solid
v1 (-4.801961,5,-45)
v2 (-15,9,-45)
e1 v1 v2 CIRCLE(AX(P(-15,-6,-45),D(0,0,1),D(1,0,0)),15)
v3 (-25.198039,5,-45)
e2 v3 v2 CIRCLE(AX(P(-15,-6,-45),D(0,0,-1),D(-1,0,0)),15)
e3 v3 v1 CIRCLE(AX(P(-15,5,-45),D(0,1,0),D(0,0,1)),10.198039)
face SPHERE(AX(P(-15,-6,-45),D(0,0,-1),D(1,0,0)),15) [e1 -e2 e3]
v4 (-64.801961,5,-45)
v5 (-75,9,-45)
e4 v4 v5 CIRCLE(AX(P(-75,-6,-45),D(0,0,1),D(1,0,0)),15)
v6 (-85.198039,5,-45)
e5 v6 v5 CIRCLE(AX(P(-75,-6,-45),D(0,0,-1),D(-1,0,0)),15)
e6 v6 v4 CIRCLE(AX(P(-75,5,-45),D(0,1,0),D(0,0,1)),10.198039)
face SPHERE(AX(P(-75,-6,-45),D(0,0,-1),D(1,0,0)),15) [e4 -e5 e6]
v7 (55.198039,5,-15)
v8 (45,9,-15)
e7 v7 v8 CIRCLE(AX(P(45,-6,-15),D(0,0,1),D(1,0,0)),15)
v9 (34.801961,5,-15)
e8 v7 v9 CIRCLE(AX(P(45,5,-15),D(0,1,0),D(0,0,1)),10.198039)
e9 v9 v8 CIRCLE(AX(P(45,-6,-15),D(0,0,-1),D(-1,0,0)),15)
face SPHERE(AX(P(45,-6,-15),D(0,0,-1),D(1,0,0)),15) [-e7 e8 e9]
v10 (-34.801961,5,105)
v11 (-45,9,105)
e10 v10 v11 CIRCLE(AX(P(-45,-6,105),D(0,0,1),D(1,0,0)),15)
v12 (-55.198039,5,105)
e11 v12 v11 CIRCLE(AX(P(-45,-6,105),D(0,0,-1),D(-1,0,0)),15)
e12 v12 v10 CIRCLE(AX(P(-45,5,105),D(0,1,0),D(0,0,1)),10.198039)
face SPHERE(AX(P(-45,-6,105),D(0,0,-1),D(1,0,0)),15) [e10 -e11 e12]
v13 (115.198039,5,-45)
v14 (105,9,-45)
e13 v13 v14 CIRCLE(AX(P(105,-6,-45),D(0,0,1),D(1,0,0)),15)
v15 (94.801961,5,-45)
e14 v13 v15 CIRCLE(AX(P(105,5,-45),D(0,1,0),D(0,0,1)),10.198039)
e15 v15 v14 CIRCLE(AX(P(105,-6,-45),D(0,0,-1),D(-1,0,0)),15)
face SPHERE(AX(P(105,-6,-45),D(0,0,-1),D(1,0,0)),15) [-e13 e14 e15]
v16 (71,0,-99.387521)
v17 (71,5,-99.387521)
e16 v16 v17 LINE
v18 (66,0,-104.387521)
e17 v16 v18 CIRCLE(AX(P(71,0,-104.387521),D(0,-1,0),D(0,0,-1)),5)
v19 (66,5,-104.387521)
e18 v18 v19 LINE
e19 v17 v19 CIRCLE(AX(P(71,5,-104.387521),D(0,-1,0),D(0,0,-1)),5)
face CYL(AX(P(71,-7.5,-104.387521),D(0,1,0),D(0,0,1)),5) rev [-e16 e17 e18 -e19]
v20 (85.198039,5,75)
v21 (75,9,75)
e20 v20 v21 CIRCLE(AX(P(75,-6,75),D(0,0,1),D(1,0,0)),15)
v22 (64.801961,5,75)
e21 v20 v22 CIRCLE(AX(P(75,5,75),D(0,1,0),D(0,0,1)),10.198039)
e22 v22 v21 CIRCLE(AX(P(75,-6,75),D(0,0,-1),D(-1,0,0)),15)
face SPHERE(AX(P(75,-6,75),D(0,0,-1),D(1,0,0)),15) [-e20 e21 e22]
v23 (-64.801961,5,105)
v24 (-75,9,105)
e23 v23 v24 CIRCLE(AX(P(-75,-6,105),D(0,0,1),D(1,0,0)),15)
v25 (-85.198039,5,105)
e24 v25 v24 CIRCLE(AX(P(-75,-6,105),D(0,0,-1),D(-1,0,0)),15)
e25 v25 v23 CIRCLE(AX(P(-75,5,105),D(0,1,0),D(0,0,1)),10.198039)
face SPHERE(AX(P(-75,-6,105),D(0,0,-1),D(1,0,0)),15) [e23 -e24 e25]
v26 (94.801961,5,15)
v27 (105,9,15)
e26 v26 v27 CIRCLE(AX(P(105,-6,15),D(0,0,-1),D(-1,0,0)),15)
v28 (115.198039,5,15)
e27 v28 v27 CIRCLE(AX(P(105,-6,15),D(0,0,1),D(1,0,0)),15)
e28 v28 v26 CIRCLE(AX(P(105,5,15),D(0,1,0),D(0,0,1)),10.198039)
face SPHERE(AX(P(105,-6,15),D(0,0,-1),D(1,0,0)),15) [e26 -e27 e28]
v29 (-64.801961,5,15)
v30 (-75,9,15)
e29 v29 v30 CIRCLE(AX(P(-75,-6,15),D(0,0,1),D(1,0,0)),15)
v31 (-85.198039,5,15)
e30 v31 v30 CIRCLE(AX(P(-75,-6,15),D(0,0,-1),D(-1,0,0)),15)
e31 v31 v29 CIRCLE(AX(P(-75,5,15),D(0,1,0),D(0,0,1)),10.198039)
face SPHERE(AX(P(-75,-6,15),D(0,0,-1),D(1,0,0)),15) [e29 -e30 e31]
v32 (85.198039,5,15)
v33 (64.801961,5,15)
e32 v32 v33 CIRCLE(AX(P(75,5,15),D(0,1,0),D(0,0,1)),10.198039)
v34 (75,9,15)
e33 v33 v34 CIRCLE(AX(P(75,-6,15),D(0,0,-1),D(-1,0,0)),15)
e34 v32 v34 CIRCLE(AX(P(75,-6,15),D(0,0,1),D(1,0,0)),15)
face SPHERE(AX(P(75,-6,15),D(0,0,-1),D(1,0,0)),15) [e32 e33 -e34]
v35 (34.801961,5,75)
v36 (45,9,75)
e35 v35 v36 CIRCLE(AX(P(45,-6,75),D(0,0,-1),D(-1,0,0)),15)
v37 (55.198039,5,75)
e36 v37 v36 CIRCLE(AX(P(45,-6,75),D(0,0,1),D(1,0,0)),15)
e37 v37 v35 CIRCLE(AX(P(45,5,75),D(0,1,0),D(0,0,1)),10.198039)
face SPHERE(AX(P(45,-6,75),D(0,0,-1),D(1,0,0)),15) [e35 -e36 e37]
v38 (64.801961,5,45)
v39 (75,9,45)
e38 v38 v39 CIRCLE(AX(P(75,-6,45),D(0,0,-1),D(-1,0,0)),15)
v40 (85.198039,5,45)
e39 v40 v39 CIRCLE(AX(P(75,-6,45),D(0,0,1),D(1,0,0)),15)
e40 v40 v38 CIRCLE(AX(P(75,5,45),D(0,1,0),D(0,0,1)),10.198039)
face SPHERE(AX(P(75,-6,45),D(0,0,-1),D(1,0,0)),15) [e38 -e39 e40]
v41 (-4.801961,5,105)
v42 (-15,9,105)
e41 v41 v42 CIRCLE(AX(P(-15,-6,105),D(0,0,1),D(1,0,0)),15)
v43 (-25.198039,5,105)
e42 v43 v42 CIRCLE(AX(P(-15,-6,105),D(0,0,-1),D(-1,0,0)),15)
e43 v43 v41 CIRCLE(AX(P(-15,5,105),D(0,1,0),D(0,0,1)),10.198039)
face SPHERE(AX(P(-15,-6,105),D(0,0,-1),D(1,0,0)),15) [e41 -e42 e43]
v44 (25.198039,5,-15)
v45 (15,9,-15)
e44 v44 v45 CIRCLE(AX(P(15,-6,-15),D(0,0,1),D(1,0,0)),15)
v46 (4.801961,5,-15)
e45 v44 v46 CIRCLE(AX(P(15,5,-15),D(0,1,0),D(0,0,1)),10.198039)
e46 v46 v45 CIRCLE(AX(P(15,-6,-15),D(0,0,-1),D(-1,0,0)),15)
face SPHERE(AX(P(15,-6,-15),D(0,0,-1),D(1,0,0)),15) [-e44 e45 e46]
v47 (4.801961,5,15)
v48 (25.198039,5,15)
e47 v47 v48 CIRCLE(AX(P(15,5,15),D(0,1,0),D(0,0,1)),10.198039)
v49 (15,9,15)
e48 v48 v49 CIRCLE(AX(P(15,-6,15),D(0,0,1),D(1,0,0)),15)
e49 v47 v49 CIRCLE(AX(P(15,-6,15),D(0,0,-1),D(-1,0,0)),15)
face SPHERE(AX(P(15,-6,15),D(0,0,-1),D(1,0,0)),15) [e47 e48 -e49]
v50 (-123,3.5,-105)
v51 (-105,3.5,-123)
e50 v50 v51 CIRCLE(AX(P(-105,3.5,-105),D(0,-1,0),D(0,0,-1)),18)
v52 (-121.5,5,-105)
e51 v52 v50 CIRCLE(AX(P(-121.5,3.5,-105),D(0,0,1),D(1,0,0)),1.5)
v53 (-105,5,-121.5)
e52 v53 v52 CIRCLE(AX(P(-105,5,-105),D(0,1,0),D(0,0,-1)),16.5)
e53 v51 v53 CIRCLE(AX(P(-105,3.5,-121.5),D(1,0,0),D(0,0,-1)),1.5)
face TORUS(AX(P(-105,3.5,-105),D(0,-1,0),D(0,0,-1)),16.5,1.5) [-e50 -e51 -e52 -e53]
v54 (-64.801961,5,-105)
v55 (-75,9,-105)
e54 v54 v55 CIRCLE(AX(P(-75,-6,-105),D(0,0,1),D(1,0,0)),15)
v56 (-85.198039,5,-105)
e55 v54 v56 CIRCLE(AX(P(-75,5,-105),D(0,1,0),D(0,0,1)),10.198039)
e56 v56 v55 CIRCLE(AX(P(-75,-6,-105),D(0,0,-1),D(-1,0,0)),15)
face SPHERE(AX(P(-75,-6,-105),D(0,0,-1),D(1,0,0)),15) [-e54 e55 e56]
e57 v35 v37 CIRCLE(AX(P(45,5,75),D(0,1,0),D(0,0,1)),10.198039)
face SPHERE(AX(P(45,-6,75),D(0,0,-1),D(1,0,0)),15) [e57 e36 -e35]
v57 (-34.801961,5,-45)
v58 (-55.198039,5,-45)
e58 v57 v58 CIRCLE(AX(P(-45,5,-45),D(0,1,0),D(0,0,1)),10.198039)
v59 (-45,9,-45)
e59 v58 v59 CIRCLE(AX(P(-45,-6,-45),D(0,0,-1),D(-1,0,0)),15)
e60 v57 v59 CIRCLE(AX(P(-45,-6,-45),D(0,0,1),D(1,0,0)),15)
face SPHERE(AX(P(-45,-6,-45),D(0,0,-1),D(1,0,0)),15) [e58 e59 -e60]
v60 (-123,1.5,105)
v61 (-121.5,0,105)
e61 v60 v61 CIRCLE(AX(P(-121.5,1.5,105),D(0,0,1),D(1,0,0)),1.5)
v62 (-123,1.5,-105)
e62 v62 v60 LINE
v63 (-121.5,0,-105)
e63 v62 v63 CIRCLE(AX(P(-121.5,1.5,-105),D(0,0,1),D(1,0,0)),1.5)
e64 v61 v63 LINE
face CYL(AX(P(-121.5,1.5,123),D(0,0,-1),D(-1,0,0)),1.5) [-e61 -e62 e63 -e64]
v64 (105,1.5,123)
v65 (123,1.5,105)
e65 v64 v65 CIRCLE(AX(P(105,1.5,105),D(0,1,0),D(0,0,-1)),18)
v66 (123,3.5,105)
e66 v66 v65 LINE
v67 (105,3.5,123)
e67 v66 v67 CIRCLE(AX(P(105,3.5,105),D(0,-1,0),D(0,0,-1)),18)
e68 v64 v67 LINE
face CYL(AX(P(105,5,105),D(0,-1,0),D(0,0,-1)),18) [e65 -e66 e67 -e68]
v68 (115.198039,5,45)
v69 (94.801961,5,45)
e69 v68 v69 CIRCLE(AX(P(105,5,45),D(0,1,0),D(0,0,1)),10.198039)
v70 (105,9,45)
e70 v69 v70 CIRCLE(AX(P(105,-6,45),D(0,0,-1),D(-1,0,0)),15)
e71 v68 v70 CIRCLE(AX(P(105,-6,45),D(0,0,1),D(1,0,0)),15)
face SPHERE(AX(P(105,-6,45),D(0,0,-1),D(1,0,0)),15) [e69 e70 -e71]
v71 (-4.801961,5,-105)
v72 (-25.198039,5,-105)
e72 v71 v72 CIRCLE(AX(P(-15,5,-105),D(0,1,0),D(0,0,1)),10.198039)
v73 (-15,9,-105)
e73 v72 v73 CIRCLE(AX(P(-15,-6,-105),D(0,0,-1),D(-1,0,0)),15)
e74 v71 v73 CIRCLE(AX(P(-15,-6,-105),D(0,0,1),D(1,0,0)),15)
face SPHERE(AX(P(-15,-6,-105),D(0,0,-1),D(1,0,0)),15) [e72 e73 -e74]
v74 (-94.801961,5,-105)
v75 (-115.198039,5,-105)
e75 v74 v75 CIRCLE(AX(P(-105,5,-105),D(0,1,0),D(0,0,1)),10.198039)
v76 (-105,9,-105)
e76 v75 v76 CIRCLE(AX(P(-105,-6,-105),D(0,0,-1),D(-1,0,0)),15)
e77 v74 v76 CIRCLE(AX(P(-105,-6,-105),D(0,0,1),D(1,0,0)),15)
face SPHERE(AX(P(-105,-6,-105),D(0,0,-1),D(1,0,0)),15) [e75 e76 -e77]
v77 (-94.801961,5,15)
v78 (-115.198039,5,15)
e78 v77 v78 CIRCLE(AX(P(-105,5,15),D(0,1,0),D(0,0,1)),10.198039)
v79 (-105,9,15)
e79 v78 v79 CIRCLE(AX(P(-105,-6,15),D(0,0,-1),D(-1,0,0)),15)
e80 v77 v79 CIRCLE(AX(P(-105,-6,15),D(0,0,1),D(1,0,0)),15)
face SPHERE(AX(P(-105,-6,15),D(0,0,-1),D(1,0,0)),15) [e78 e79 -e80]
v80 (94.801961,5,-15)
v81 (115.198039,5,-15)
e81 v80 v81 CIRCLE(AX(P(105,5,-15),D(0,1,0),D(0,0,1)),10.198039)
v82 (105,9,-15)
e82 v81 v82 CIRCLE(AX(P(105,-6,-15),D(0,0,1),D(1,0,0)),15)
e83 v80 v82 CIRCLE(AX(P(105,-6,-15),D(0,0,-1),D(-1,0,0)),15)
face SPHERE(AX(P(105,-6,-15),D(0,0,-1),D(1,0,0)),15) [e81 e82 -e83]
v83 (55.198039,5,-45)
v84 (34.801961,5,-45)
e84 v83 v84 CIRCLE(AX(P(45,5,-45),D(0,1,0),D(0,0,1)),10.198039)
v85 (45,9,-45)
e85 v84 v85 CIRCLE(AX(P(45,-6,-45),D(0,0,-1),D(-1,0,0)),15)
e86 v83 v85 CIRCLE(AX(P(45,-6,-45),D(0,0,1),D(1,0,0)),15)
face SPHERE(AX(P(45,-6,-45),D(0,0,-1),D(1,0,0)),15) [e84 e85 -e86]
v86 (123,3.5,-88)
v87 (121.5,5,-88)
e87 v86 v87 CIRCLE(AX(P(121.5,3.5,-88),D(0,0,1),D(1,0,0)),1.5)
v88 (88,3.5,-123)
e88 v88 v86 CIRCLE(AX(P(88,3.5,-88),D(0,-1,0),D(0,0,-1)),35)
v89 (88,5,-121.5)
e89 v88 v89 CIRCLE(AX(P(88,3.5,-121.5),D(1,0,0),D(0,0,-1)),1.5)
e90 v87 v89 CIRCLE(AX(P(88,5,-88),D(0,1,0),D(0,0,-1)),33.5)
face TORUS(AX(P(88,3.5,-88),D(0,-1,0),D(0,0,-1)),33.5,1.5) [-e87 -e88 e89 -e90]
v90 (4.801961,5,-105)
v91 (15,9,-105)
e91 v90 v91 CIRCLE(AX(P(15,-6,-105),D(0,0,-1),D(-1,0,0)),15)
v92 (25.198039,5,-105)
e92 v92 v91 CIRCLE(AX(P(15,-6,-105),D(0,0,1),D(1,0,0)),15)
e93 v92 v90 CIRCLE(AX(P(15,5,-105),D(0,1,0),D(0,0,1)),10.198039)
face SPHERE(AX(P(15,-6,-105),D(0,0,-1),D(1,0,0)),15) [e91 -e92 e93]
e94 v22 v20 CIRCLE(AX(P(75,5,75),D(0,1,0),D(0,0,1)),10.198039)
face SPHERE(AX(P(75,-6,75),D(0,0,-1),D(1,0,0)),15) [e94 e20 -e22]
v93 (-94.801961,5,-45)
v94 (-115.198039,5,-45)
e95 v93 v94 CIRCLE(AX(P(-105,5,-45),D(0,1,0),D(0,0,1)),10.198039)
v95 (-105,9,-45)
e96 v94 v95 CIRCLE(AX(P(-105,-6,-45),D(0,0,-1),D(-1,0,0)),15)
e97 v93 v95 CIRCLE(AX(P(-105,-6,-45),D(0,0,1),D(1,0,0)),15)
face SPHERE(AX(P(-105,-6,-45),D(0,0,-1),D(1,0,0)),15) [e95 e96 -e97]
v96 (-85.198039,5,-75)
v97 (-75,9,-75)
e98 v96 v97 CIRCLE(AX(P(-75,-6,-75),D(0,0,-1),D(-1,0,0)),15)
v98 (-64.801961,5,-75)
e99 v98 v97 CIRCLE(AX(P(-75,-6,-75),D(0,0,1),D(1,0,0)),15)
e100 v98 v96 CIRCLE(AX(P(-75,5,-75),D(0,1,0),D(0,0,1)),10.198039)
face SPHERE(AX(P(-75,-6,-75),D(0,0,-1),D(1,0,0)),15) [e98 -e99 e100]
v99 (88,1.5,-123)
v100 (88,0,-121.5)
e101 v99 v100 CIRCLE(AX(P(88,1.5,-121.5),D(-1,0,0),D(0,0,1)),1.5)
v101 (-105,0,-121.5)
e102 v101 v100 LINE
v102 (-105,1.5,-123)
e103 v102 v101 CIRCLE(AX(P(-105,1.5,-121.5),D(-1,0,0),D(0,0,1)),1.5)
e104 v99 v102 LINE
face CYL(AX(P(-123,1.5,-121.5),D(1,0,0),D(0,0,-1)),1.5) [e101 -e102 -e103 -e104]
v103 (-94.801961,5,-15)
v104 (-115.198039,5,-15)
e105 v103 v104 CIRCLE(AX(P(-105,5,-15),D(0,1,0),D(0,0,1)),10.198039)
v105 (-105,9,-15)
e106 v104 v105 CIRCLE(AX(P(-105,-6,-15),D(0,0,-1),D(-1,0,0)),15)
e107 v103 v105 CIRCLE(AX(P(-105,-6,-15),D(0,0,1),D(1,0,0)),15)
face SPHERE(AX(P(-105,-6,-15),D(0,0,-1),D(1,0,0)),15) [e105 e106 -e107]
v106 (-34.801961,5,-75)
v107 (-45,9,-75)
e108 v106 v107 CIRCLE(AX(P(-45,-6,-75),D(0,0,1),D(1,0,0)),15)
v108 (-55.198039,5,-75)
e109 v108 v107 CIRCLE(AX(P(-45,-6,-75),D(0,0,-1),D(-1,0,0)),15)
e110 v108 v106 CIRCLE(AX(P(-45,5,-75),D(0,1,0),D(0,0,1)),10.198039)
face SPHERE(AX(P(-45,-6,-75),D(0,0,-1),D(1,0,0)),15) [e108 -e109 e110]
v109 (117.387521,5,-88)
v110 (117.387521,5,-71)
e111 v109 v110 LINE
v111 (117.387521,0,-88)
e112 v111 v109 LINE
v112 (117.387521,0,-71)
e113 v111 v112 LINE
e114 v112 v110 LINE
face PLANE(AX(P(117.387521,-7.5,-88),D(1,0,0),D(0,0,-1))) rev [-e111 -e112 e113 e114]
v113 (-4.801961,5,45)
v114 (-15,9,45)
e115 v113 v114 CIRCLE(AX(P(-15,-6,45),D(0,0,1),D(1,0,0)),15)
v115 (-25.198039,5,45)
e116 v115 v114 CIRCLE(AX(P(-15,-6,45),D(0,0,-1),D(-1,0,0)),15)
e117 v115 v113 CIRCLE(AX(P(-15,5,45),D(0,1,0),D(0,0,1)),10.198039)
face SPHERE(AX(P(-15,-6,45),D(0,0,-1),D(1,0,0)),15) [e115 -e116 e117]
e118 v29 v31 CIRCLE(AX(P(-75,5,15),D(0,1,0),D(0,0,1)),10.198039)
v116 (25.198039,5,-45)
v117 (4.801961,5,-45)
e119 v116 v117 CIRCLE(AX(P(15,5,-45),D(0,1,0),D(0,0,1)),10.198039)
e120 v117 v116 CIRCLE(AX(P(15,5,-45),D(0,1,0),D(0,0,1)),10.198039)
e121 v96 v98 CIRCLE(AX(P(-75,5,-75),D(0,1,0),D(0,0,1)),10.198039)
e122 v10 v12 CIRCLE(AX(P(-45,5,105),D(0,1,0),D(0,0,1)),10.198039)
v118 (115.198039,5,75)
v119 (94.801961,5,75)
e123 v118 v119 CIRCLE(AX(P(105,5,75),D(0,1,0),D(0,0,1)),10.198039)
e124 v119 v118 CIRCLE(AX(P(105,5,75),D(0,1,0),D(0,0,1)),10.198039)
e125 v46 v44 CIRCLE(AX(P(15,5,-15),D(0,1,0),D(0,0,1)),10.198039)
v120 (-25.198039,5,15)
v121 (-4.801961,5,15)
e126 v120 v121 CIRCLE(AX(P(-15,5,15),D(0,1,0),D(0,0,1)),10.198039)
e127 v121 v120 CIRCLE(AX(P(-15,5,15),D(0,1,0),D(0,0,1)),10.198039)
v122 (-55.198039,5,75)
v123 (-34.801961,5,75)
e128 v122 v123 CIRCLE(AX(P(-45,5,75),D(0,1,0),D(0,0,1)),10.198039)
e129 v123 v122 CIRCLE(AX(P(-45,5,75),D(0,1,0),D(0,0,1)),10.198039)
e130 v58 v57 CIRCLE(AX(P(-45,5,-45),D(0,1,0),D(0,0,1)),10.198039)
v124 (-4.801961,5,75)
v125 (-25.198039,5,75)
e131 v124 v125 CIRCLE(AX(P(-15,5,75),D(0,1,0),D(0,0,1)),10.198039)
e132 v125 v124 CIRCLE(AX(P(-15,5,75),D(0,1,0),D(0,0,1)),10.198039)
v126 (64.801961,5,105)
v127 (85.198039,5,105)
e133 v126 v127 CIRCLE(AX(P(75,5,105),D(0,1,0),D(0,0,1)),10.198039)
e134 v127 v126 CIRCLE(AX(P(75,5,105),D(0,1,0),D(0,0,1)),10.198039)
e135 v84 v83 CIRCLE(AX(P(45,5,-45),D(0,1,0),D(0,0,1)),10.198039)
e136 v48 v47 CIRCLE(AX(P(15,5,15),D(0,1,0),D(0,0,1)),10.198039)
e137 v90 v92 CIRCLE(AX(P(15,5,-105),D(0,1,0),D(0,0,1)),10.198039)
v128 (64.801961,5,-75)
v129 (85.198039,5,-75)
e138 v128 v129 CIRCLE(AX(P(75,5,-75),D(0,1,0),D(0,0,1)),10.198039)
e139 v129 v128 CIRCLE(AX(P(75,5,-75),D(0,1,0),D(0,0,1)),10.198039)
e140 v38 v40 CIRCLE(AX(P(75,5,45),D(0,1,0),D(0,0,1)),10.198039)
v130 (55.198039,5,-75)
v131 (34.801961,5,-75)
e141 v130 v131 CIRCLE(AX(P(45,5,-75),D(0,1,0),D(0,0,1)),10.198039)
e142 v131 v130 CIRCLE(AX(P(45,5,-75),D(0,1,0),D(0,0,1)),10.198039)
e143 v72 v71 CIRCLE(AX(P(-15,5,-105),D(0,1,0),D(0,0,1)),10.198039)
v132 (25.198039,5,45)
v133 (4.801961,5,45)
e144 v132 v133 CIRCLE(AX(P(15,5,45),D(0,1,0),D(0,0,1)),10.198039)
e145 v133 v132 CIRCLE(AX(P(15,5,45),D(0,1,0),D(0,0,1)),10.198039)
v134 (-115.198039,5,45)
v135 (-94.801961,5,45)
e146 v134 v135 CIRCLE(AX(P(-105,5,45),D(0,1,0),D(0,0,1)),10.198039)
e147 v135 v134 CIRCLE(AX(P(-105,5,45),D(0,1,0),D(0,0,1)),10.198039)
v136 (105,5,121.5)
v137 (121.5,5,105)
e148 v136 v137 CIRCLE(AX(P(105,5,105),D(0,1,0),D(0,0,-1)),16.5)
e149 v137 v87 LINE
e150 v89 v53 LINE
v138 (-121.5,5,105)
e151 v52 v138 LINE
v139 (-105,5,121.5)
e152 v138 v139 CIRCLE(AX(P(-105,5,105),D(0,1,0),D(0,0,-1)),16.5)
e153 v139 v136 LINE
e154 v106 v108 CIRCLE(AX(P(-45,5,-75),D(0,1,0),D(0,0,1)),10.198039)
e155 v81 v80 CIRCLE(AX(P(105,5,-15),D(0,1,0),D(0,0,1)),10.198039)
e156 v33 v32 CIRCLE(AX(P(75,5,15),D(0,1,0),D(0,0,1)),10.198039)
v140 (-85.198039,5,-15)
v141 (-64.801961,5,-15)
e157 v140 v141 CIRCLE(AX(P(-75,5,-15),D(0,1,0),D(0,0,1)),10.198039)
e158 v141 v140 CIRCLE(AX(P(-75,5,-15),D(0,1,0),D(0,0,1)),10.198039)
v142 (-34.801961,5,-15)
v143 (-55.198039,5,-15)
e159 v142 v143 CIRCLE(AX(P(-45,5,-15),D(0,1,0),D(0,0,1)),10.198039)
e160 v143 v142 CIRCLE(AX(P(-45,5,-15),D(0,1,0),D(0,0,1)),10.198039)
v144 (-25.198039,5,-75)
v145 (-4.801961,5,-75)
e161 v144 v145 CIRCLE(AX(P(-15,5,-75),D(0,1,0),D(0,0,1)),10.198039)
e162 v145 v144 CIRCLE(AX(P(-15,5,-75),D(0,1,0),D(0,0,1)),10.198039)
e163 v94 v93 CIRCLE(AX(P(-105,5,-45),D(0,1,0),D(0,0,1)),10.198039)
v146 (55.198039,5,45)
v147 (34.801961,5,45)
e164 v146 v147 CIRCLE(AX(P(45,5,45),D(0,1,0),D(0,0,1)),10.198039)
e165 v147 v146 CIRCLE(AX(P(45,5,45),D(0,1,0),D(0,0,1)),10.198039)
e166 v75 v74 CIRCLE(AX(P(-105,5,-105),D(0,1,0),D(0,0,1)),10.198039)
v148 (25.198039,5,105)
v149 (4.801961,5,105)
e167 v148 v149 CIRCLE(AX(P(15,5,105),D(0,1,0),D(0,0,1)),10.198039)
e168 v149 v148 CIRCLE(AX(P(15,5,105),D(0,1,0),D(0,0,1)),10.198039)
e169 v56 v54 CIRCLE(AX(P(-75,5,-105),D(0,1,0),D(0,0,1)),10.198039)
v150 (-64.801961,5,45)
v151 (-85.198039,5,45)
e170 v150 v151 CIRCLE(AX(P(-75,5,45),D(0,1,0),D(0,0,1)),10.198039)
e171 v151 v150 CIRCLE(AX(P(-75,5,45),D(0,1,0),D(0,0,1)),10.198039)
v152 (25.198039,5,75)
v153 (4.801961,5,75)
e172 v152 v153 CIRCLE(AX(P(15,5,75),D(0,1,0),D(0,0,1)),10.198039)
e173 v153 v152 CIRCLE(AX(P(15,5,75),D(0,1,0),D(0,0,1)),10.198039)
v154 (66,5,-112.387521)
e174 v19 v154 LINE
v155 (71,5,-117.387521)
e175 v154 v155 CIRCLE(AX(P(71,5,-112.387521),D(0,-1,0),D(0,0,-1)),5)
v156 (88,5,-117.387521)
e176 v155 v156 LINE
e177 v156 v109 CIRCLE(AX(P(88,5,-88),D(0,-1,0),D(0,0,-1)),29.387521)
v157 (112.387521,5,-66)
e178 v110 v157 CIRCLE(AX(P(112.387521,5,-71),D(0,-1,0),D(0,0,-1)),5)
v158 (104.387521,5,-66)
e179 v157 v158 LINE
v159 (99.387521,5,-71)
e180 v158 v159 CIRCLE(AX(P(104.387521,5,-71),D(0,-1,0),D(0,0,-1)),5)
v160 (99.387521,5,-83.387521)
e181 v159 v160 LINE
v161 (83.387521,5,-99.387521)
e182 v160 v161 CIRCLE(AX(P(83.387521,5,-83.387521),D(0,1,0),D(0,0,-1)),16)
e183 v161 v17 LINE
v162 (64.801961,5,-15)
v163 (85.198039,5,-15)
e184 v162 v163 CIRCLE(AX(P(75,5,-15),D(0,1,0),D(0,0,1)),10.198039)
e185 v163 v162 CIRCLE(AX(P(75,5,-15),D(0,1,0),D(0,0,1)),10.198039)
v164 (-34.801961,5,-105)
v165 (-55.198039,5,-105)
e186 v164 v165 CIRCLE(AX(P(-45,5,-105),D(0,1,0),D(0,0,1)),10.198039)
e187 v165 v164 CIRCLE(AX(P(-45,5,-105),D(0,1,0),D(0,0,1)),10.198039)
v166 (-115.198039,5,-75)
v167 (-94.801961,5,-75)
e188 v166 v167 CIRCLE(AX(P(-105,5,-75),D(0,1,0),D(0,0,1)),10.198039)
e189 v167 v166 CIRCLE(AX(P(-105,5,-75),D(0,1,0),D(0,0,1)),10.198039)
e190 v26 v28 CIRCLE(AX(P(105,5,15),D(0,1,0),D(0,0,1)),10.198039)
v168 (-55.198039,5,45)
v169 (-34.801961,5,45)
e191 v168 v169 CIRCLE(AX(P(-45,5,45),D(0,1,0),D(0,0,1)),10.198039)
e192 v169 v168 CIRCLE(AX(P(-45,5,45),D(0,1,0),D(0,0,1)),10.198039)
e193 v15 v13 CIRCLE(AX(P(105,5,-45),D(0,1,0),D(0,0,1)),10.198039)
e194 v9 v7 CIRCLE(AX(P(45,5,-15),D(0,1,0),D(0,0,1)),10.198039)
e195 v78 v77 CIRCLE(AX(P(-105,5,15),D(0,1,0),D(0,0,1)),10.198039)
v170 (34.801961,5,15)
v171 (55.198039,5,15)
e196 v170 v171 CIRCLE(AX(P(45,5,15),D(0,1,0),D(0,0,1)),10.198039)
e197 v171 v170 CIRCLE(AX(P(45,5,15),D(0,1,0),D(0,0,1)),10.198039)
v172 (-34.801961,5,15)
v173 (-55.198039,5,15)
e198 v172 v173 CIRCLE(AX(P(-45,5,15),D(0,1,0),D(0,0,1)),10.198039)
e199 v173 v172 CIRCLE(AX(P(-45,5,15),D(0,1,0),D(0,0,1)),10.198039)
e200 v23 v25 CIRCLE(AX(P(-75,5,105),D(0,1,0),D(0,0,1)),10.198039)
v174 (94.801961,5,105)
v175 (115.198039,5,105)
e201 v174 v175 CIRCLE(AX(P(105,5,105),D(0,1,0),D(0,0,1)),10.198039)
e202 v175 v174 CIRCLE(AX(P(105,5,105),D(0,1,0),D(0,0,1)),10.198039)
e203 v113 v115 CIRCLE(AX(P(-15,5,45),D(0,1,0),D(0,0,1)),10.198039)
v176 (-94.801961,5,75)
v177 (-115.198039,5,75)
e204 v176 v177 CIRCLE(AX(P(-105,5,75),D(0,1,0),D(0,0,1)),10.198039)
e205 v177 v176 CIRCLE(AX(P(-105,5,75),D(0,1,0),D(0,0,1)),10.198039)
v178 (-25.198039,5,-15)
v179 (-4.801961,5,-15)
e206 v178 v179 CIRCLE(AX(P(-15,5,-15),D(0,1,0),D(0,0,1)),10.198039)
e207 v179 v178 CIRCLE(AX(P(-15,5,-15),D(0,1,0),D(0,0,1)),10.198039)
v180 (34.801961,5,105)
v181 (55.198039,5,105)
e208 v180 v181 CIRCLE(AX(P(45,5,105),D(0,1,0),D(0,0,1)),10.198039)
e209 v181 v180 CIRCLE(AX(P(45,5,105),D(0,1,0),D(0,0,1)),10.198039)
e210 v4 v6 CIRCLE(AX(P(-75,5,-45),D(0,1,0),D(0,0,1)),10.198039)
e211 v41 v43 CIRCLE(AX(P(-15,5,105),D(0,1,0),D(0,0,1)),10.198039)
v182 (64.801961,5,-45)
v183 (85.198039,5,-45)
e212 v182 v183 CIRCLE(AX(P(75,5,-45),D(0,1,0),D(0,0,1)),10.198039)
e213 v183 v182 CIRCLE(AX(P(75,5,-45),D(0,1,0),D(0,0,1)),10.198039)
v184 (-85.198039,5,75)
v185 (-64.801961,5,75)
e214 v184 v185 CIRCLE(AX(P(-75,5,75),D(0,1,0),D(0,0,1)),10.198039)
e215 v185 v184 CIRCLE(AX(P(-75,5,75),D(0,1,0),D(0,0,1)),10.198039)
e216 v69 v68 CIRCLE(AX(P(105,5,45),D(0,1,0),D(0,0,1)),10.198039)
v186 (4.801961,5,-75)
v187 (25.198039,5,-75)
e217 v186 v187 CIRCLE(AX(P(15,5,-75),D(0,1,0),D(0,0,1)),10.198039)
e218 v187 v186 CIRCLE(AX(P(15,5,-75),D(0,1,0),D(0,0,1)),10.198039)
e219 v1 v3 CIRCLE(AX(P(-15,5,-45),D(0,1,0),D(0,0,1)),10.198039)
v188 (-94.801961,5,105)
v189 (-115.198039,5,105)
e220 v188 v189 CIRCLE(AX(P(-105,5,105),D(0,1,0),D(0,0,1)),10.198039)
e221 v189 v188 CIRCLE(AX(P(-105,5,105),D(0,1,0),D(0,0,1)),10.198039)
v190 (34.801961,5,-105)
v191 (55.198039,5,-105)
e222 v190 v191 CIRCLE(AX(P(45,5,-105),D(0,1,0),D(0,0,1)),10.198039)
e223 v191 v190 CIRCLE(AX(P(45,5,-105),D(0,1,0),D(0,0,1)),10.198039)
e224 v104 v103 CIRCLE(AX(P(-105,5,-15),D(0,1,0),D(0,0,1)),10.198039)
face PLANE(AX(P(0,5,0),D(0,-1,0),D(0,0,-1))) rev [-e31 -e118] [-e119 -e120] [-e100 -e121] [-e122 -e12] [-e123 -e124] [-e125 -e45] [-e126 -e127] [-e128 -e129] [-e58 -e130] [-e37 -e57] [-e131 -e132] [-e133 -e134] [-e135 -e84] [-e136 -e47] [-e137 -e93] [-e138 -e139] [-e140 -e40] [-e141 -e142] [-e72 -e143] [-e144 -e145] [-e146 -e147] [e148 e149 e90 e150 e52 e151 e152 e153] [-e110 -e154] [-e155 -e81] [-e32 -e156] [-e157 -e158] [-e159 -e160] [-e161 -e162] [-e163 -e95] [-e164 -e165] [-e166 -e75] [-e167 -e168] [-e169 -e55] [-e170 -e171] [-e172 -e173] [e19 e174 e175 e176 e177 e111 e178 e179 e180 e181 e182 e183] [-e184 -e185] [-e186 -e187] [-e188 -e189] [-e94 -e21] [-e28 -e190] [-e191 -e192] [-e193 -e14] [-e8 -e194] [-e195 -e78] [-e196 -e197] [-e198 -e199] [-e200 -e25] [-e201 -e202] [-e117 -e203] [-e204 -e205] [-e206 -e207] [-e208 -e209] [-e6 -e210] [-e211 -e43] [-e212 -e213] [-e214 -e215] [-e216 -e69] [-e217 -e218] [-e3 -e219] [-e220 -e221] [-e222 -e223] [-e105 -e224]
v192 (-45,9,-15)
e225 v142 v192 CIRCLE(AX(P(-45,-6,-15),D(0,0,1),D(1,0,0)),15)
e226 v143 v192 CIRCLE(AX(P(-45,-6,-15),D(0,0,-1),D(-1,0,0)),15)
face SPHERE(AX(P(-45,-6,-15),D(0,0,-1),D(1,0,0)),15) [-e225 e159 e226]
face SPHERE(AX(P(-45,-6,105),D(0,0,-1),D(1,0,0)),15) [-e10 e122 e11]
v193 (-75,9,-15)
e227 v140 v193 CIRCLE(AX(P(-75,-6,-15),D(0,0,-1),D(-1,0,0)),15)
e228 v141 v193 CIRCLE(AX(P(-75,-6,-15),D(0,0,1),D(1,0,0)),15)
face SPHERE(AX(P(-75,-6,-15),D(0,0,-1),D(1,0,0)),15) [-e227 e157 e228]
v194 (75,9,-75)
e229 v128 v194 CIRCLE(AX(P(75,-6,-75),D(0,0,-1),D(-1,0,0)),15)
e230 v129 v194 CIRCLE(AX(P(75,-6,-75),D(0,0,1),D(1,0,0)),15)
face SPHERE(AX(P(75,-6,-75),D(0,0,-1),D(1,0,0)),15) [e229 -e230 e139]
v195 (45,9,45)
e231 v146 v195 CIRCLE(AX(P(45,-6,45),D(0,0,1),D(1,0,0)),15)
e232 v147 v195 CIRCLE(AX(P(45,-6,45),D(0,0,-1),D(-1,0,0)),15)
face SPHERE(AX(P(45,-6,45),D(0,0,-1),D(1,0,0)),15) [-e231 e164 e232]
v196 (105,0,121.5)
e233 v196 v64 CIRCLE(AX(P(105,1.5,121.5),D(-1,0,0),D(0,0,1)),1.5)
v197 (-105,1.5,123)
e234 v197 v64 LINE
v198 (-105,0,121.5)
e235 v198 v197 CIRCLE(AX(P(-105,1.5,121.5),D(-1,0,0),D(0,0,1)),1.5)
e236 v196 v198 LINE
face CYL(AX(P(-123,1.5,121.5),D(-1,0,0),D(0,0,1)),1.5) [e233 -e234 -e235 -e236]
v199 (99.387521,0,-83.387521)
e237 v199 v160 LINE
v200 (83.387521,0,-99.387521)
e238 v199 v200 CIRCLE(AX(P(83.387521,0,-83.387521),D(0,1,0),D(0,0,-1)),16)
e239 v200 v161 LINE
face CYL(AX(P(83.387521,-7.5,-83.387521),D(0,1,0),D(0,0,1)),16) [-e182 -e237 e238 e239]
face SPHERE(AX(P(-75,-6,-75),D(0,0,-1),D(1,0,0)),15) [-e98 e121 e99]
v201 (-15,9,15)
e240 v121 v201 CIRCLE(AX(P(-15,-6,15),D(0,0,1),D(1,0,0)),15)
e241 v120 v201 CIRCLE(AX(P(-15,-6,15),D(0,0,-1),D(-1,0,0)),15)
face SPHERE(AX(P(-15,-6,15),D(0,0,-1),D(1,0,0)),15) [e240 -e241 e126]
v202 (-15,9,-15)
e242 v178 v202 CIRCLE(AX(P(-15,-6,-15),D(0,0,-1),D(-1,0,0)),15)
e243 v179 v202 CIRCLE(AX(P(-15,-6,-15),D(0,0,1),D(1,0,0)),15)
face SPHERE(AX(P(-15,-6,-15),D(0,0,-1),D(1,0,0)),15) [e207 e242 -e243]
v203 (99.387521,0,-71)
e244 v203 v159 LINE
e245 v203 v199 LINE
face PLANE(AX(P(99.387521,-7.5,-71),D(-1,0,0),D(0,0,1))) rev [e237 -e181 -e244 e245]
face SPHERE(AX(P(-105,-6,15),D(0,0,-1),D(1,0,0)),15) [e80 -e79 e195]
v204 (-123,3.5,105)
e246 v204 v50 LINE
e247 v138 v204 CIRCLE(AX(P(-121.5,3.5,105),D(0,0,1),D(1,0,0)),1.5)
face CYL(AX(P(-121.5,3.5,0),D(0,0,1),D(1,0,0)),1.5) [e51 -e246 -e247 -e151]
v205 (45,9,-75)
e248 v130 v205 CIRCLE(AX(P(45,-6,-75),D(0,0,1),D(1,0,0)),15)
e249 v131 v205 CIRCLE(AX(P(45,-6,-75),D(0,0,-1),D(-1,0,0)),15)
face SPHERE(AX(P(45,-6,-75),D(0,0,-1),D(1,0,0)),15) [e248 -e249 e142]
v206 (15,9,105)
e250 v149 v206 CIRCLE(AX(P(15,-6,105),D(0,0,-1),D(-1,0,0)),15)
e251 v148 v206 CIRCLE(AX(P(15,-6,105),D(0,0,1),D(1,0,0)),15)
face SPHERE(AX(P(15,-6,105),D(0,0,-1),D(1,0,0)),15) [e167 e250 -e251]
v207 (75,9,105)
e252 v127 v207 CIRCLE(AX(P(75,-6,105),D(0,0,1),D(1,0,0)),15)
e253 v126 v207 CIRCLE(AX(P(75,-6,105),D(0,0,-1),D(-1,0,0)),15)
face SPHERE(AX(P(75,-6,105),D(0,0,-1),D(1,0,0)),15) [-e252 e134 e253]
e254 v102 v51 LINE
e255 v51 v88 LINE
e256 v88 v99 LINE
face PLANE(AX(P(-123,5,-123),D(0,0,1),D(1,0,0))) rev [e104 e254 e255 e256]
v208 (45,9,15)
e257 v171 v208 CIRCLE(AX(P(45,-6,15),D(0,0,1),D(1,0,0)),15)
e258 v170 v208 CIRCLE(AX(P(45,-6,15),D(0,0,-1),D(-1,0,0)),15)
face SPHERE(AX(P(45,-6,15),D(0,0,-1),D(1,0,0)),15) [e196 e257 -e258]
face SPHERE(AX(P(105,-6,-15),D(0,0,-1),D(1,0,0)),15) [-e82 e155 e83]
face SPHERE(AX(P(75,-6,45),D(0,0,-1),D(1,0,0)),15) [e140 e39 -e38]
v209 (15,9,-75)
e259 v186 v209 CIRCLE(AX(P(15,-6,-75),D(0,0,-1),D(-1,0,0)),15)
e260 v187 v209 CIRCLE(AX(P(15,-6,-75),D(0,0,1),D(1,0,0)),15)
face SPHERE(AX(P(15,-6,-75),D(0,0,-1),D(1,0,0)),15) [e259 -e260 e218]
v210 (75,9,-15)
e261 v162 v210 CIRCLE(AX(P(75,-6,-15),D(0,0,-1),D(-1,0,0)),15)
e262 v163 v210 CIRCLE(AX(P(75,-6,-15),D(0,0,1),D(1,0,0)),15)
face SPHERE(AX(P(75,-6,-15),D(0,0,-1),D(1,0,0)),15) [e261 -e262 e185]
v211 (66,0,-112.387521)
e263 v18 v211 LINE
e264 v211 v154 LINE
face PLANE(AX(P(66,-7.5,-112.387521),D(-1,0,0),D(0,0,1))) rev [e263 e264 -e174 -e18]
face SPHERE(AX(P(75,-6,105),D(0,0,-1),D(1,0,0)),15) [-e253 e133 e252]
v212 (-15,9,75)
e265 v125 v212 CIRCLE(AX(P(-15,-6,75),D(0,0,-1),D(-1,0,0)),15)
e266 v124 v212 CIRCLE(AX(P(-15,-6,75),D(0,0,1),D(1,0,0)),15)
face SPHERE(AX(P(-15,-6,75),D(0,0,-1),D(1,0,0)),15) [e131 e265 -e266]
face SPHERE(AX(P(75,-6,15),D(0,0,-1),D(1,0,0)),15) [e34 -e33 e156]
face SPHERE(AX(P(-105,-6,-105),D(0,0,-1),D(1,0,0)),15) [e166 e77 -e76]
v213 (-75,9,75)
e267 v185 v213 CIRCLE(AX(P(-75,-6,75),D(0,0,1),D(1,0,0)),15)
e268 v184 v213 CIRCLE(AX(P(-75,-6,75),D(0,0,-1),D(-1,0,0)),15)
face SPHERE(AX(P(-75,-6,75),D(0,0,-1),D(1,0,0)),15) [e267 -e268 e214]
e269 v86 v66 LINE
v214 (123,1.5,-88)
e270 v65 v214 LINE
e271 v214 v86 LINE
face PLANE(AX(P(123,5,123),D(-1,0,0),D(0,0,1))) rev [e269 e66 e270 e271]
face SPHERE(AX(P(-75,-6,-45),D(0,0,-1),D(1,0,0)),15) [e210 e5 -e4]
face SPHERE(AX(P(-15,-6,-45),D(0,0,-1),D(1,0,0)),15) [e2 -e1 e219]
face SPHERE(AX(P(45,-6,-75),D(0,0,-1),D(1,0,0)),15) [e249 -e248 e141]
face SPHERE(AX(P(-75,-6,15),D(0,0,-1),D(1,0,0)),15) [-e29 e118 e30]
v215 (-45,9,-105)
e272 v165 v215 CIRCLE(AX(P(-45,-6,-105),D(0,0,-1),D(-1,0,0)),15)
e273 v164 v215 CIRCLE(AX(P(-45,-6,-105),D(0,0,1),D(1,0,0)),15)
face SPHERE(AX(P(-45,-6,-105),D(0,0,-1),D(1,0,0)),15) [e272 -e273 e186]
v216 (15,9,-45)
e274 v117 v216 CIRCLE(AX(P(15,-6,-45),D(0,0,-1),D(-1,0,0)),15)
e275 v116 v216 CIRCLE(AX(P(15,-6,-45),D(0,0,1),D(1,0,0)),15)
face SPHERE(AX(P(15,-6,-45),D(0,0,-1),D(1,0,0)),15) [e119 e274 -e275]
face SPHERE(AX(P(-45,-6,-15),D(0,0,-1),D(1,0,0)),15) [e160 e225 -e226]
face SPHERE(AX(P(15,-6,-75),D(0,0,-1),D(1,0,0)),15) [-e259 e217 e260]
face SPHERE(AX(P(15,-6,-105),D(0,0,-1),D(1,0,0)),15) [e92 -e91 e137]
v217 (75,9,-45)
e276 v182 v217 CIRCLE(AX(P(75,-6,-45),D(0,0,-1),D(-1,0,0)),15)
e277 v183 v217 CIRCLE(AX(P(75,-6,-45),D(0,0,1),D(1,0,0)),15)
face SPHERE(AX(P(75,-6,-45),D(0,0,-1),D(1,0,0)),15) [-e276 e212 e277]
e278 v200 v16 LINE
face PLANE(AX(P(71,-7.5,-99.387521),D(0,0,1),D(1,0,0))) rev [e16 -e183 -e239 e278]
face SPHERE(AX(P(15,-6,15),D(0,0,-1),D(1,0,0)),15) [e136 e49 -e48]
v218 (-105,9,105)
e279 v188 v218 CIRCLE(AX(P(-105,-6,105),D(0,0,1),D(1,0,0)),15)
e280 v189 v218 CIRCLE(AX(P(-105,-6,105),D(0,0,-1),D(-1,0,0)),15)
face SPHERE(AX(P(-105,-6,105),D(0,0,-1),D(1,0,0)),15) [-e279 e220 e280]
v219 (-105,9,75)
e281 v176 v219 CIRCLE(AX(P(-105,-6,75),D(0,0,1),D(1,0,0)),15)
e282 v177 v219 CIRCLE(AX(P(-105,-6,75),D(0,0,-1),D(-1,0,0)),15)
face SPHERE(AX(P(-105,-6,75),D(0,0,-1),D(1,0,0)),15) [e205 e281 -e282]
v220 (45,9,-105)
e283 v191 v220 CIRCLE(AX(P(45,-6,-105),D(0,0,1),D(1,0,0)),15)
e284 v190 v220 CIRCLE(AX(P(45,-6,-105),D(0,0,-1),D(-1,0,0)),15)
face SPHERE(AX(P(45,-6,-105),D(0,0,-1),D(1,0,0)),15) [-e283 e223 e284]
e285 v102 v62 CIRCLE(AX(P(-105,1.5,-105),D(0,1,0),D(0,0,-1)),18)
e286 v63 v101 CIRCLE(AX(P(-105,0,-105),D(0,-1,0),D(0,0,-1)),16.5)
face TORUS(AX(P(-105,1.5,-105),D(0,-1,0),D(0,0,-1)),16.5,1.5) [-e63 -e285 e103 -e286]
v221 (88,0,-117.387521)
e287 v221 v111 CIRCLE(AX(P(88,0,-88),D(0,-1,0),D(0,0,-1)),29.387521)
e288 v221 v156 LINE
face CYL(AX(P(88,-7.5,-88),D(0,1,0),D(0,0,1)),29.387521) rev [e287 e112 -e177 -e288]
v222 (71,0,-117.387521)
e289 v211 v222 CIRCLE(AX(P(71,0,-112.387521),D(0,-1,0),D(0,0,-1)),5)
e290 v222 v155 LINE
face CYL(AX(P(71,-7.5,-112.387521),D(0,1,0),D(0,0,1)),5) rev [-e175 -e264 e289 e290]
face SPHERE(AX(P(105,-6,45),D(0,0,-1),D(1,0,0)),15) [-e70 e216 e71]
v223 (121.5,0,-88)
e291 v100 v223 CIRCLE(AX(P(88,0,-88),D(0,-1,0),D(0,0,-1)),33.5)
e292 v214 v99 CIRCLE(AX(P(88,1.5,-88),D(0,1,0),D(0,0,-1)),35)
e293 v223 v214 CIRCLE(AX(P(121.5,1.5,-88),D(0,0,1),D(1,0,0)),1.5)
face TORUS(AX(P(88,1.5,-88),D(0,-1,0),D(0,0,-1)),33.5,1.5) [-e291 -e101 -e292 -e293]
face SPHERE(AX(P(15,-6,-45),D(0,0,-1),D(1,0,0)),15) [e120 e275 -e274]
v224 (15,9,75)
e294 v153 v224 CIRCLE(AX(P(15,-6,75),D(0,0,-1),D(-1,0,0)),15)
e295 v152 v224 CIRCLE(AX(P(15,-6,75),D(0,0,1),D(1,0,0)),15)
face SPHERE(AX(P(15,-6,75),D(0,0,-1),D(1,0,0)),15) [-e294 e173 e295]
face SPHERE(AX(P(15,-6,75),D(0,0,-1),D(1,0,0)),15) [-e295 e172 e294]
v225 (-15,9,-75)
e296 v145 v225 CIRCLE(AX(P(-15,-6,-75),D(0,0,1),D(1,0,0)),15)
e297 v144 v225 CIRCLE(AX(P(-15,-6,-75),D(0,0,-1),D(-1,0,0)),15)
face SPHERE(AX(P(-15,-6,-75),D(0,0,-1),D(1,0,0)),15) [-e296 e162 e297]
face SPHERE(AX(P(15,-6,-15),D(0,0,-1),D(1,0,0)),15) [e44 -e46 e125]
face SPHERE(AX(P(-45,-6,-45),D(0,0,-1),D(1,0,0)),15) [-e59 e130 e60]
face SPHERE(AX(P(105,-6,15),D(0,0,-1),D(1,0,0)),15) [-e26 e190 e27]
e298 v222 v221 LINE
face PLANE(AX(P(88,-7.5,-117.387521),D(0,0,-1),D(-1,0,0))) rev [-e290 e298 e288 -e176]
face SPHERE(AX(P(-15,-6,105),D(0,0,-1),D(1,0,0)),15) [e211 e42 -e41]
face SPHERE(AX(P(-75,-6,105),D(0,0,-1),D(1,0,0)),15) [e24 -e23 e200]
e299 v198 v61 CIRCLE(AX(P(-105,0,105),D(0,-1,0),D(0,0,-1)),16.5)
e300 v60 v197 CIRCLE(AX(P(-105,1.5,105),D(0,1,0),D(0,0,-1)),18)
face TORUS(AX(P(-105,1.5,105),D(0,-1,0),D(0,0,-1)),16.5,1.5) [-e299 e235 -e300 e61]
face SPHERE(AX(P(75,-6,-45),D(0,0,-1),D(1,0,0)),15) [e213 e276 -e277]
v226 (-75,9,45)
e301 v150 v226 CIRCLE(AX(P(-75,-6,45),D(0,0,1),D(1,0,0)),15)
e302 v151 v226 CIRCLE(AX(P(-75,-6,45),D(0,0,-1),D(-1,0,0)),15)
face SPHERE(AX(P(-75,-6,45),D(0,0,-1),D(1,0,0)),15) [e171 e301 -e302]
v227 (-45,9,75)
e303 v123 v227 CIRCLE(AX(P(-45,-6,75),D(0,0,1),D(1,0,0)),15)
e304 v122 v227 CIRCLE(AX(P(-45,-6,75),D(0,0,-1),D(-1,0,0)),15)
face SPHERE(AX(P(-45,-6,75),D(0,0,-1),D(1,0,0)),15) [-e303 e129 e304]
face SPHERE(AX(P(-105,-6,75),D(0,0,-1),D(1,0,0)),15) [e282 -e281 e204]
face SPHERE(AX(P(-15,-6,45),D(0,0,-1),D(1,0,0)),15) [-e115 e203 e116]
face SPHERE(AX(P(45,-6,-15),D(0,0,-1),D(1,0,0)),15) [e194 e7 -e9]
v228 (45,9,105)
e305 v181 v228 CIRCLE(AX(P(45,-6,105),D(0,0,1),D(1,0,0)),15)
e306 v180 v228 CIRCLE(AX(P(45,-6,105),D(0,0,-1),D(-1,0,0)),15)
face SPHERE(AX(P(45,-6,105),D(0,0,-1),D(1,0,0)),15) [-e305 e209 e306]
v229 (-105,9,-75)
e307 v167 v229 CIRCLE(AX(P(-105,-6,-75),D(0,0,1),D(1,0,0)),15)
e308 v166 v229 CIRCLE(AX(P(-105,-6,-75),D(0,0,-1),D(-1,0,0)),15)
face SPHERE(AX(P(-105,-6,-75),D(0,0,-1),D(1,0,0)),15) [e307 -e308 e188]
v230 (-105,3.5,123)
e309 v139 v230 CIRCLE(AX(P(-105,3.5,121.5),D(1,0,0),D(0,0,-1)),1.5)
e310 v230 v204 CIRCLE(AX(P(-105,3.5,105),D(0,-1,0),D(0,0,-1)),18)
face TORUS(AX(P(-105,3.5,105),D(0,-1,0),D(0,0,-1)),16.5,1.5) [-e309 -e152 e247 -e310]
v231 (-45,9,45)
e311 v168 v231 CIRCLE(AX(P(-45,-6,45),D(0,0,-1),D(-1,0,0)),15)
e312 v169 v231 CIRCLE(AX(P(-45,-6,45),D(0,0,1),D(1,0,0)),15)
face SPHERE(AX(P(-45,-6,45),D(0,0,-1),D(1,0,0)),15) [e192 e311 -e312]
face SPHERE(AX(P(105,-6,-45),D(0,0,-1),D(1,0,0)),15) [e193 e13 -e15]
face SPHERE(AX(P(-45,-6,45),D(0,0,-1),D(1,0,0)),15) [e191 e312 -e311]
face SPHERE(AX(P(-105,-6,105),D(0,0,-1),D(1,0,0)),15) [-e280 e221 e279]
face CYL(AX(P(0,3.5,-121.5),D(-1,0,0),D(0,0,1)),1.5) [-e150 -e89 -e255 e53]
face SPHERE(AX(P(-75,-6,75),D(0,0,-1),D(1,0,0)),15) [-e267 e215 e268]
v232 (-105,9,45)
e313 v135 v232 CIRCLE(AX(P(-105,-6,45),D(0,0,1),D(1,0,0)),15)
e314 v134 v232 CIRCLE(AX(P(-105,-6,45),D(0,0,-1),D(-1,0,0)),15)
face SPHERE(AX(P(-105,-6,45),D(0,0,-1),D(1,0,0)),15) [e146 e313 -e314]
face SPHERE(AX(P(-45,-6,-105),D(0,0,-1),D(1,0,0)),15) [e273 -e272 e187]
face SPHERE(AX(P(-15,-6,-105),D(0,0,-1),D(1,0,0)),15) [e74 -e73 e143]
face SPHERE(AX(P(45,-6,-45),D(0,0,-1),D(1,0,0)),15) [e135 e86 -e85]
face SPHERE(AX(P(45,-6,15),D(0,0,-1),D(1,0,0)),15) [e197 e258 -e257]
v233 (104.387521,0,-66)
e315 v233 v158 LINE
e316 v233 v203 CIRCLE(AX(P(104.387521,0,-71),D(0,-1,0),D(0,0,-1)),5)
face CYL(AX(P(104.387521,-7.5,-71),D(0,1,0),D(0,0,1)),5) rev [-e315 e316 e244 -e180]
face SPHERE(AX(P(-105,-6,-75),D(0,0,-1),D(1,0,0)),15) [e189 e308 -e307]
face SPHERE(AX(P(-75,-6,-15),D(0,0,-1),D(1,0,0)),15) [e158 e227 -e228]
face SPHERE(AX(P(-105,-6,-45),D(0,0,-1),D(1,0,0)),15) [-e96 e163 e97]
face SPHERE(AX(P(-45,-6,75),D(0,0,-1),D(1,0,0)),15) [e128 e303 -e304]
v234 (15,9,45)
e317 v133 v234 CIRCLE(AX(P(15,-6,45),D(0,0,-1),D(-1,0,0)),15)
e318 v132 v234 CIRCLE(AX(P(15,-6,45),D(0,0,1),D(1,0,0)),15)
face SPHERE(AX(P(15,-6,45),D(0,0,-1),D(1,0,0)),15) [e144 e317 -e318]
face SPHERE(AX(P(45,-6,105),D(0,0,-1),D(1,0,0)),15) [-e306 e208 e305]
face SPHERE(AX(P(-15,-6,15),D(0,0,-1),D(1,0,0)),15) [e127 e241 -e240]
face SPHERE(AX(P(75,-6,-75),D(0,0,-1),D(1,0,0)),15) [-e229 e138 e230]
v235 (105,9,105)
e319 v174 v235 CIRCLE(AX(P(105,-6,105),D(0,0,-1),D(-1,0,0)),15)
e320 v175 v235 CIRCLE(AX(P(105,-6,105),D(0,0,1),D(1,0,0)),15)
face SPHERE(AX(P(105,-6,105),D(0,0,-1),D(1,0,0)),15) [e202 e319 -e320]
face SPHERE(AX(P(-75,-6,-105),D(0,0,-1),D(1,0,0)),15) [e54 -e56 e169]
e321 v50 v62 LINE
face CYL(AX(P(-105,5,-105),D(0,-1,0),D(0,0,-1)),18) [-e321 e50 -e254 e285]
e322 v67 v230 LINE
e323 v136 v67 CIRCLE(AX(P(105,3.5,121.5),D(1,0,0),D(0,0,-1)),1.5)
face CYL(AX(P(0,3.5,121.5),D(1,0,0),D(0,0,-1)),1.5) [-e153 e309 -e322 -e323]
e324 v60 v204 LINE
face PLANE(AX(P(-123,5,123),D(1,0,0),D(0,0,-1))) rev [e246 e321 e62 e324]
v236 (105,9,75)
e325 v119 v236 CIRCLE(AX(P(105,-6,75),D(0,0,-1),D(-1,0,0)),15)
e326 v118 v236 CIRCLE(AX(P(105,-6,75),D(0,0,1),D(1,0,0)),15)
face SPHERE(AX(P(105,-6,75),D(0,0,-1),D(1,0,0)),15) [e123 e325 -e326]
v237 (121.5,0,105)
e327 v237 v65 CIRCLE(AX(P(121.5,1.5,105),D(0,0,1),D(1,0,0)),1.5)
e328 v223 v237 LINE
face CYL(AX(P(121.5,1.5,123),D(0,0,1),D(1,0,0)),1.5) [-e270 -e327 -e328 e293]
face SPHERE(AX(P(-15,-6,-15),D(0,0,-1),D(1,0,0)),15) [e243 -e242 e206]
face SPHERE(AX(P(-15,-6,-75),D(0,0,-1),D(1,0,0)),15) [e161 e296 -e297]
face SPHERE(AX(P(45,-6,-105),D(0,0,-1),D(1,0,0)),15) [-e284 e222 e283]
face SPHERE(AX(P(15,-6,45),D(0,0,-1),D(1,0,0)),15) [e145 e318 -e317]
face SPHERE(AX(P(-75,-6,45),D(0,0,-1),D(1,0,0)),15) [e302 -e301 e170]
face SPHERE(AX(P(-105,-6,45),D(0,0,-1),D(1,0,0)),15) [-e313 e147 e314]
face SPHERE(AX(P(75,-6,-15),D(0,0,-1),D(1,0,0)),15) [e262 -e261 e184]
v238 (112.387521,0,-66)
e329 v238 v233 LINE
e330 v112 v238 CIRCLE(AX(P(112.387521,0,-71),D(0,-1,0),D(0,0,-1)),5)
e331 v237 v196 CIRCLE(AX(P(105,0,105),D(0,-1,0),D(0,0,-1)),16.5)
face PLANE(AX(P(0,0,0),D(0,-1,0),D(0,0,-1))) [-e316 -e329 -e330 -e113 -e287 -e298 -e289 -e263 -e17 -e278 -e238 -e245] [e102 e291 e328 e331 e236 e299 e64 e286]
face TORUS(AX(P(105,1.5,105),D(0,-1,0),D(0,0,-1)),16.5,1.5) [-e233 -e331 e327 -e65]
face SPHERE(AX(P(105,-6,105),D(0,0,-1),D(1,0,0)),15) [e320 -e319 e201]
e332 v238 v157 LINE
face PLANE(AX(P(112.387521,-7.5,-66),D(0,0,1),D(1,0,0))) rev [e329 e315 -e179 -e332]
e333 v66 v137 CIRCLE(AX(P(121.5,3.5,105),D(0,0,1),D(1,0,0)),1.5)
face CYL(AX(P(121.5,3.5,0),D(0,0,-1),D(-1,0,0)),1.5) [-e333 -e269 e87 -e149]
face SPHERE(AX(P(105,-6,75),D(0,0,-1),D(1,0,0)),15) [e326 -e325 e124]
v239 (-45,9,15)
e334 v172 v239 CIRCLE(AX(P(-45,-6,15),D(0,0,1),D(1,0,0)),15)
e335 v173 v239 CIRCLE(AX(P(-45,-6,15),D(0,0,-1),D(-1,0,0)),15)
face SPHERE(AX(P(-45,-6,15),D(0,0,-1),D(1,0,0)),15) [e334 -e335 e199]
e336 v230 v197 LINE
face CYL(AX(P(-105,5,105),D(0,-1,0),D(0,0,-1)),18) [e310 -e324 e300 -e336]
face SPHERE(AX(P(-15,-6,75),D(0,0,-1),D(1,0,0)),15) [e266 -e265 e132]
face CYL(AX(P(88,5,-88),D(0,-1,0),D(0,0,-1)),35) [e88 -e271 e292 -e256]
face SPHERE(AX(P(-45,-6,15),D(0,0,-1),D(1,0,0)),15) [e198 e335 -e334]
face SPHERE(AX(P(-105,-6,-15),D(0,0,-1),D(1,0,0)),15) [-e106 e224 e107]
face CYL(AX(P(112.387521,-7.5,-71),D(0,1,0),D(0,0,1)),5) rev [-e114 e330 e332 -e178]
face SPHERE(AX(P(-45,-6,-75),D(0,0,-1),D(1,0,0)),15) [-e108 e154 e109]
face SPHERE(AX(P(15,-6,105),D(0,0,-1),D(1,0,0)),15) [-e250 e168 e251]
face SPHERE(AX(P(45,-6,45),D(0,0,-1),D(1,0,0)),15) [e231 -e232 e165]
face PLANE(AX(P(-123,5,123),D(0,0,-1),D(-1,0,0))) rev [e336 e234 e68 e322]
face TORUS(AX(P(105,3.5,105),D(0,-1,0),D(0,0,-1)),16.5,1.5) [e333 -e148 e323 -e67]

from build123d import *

# Parameters (mm, degrees)
PLATE_PROFILE_SKETCH_W                 = 246
PLATE_PROFILE_SKETCH_H                 = 246
BASE_PLATE_246X246X5_DEPTH             = 5
CORNER_FILLETS_R35_R                   = 35
HANGING_SLOT_CUT_DEPTH                 = 12.5
EDGE_FILLET_R18_R                      = 18
DOME_PATTERN_8X8_30MM_PITCH_COUNT      = 8
DOME_PATTERN_8X8_30MM_PITCH_PITCH      = 30
DOME_PATTERN_8X8_30MM_PITCH_COUNT_DIR2 = 8
DOME_PATTERN_8X8_30MM_PITCH_PITCH_DIR2 = 30
EDGE_FILLETS_R1_5_R                    = 1.5


with BuildPart() as part:
    # Plate Profile Sketch → Base Plate 246x246x5 (new body)
    with BuildSketch(Plane(origin=(0, 0, 0), x_dir=(1, 0, 0), z_dir=(0, 1, 0))):
        Rectangle(PLATE_PROFILE_SKETCH_W, PLATE_PROFILE_SKETCH_H)
    extrude(amount=BASE_PLATE_246X246X5_DEPTH)

    # Corner Fillets R35
    corner_fillets_r35_edges = [part.edges().sort_by_distance(p)[0] for p in [
        (123, 2.5, -123),
    ]]
    fillet(corner_fillets_r35_edges, radius=CORNER_FILLETS_R35_R)

    # Hanging Slot Sketch → Hanging Slot Cut (cut, symmetric)
    with BuildSketch(Plane(origin=(0, 5, 0), x_dir=(1, 0, 0), z_dir=(0, 1, 0))):
        with BuildLine():
            Line((88, 117.387520694), (71, 117.387520694))
            ThreePointArc((71, 117.387520694), (67.464466094, 115.9230546), (66, 112.387520694))
            Line((66, 112.387520694), (66, 104.387520694))
            ThreePointArc((66, 104.387520694), (67.464466094, 100.851986788), (71, 99.387520694))
            Line((71, 99.387520694), (83.387520694, 99.387520694))
            ThreePointArc((83.387520694, 99.387520694), (94.701229193, 94.701229193), (99.387520694, 83.387520694))
            Line((99.387520694, 83.387520694), (99.387520694, 71))
            ThreePointArc((99.387520694, 71), (100.851986788, 67.464466094), (104.387520694, 66))
            Line((104.387520694, 66), (112.387520694, 66))
            ThreePointArc((112.387520694, 66), (115.9230546, 67.464466094), (117.387520694, 71))
            Line((117.387520694, 71), (117.387520694, 88))
            ThreePointArc((117.387520694, 88), (108.780115165, 108.780115165), (88, 117.387520694))
        make_face()
    extrude(amount=HANGING_SLOT_CUT_DEPTH, both=True, mode=Mode.SUBTRACT)

    # Edge Fillet R18
    edge_fillet_r18_edges = [part.edges().sort_by_distance(p)[0] for p in [
        (123, 2.5, 123),
        (-123, 2.5, 123),
        (-123, 2.5, -123),
    ]]
    fillet(edge_fillet_r18_edges, radius=EDGE_FILLET_R18_R)

    # Dome Profile Sketch → Dome Boss (revolve)
    with BuildSketch(Plane.XY.offset(105), mode=Mode.PRIVATE) as dome_boss_sk:
        with BuildLine():
            Line((105, 9), (105, 5))
            Line((105, 5), (94.801960973, 5))
            ThreePointArc((94.801960973, 5), (99.522774425, 7.964240044), (105, 9))
        make_face()
    dome_boss = revolve(dome_boss_sk.sketch.rotate(Axis((105, 9, 105), (0, -1, 0)), 180), axis=Axis((105, 9, 105), (0, -1, 0)))

    # Dome Pattern 8x8 30mm Pitch: Dome Boss 8 × 8, 3 skipped
    with Locations(*[(-j * DOME_PATTERN_8X8_30MM_PITCH_PITCH_DIR2, 0, -i * DOME_PATTERN_8X8_30MM_PITCH_PITCH) for i in range(DOME_PATTERN_8X8_30MM_PITCH_COUNT) for j in range(DOME_PATTERN_8X8_30MM_PITCH_COUNT_DIR2) if (i, j) not in ((0, 0), (6, 0), (7, 0), (7, 1))]):
        add(dome_boss)

    # Edge Fillets R1.5
    edge_fillets_r1_5_edges = [part.edges().sort_by_distance(p)[0] for p in [
        (123, 5, 8.5),
        (0, 5, 123),
        (117.727922061, 5, 117.727922061),
        (-117.727922061, 5, 117.727922061),
        (-117.727922061, 5, -117.727922061),
        (-8.5, 0, -123),
        (-8.5, 5, -123),
        (112.748737342, 0, -112.748737342),
        (112.748737342, 5, -112.748737342),
        (-123, 0, 0),
        (-123, 5, 0),
        (123, 0, 8.5),
        (0, 0, 123),
        (117.727922061, 0, 117.727922061),
        (-117.727922061, 0, 117.727922061),
        (-117.727922061, 0, -117.727922061),
    ]]
    fillet(edge_fillets_r1_5_edges, radius=EDGE_FILLETS_R1_5_R)


solid = part.part
